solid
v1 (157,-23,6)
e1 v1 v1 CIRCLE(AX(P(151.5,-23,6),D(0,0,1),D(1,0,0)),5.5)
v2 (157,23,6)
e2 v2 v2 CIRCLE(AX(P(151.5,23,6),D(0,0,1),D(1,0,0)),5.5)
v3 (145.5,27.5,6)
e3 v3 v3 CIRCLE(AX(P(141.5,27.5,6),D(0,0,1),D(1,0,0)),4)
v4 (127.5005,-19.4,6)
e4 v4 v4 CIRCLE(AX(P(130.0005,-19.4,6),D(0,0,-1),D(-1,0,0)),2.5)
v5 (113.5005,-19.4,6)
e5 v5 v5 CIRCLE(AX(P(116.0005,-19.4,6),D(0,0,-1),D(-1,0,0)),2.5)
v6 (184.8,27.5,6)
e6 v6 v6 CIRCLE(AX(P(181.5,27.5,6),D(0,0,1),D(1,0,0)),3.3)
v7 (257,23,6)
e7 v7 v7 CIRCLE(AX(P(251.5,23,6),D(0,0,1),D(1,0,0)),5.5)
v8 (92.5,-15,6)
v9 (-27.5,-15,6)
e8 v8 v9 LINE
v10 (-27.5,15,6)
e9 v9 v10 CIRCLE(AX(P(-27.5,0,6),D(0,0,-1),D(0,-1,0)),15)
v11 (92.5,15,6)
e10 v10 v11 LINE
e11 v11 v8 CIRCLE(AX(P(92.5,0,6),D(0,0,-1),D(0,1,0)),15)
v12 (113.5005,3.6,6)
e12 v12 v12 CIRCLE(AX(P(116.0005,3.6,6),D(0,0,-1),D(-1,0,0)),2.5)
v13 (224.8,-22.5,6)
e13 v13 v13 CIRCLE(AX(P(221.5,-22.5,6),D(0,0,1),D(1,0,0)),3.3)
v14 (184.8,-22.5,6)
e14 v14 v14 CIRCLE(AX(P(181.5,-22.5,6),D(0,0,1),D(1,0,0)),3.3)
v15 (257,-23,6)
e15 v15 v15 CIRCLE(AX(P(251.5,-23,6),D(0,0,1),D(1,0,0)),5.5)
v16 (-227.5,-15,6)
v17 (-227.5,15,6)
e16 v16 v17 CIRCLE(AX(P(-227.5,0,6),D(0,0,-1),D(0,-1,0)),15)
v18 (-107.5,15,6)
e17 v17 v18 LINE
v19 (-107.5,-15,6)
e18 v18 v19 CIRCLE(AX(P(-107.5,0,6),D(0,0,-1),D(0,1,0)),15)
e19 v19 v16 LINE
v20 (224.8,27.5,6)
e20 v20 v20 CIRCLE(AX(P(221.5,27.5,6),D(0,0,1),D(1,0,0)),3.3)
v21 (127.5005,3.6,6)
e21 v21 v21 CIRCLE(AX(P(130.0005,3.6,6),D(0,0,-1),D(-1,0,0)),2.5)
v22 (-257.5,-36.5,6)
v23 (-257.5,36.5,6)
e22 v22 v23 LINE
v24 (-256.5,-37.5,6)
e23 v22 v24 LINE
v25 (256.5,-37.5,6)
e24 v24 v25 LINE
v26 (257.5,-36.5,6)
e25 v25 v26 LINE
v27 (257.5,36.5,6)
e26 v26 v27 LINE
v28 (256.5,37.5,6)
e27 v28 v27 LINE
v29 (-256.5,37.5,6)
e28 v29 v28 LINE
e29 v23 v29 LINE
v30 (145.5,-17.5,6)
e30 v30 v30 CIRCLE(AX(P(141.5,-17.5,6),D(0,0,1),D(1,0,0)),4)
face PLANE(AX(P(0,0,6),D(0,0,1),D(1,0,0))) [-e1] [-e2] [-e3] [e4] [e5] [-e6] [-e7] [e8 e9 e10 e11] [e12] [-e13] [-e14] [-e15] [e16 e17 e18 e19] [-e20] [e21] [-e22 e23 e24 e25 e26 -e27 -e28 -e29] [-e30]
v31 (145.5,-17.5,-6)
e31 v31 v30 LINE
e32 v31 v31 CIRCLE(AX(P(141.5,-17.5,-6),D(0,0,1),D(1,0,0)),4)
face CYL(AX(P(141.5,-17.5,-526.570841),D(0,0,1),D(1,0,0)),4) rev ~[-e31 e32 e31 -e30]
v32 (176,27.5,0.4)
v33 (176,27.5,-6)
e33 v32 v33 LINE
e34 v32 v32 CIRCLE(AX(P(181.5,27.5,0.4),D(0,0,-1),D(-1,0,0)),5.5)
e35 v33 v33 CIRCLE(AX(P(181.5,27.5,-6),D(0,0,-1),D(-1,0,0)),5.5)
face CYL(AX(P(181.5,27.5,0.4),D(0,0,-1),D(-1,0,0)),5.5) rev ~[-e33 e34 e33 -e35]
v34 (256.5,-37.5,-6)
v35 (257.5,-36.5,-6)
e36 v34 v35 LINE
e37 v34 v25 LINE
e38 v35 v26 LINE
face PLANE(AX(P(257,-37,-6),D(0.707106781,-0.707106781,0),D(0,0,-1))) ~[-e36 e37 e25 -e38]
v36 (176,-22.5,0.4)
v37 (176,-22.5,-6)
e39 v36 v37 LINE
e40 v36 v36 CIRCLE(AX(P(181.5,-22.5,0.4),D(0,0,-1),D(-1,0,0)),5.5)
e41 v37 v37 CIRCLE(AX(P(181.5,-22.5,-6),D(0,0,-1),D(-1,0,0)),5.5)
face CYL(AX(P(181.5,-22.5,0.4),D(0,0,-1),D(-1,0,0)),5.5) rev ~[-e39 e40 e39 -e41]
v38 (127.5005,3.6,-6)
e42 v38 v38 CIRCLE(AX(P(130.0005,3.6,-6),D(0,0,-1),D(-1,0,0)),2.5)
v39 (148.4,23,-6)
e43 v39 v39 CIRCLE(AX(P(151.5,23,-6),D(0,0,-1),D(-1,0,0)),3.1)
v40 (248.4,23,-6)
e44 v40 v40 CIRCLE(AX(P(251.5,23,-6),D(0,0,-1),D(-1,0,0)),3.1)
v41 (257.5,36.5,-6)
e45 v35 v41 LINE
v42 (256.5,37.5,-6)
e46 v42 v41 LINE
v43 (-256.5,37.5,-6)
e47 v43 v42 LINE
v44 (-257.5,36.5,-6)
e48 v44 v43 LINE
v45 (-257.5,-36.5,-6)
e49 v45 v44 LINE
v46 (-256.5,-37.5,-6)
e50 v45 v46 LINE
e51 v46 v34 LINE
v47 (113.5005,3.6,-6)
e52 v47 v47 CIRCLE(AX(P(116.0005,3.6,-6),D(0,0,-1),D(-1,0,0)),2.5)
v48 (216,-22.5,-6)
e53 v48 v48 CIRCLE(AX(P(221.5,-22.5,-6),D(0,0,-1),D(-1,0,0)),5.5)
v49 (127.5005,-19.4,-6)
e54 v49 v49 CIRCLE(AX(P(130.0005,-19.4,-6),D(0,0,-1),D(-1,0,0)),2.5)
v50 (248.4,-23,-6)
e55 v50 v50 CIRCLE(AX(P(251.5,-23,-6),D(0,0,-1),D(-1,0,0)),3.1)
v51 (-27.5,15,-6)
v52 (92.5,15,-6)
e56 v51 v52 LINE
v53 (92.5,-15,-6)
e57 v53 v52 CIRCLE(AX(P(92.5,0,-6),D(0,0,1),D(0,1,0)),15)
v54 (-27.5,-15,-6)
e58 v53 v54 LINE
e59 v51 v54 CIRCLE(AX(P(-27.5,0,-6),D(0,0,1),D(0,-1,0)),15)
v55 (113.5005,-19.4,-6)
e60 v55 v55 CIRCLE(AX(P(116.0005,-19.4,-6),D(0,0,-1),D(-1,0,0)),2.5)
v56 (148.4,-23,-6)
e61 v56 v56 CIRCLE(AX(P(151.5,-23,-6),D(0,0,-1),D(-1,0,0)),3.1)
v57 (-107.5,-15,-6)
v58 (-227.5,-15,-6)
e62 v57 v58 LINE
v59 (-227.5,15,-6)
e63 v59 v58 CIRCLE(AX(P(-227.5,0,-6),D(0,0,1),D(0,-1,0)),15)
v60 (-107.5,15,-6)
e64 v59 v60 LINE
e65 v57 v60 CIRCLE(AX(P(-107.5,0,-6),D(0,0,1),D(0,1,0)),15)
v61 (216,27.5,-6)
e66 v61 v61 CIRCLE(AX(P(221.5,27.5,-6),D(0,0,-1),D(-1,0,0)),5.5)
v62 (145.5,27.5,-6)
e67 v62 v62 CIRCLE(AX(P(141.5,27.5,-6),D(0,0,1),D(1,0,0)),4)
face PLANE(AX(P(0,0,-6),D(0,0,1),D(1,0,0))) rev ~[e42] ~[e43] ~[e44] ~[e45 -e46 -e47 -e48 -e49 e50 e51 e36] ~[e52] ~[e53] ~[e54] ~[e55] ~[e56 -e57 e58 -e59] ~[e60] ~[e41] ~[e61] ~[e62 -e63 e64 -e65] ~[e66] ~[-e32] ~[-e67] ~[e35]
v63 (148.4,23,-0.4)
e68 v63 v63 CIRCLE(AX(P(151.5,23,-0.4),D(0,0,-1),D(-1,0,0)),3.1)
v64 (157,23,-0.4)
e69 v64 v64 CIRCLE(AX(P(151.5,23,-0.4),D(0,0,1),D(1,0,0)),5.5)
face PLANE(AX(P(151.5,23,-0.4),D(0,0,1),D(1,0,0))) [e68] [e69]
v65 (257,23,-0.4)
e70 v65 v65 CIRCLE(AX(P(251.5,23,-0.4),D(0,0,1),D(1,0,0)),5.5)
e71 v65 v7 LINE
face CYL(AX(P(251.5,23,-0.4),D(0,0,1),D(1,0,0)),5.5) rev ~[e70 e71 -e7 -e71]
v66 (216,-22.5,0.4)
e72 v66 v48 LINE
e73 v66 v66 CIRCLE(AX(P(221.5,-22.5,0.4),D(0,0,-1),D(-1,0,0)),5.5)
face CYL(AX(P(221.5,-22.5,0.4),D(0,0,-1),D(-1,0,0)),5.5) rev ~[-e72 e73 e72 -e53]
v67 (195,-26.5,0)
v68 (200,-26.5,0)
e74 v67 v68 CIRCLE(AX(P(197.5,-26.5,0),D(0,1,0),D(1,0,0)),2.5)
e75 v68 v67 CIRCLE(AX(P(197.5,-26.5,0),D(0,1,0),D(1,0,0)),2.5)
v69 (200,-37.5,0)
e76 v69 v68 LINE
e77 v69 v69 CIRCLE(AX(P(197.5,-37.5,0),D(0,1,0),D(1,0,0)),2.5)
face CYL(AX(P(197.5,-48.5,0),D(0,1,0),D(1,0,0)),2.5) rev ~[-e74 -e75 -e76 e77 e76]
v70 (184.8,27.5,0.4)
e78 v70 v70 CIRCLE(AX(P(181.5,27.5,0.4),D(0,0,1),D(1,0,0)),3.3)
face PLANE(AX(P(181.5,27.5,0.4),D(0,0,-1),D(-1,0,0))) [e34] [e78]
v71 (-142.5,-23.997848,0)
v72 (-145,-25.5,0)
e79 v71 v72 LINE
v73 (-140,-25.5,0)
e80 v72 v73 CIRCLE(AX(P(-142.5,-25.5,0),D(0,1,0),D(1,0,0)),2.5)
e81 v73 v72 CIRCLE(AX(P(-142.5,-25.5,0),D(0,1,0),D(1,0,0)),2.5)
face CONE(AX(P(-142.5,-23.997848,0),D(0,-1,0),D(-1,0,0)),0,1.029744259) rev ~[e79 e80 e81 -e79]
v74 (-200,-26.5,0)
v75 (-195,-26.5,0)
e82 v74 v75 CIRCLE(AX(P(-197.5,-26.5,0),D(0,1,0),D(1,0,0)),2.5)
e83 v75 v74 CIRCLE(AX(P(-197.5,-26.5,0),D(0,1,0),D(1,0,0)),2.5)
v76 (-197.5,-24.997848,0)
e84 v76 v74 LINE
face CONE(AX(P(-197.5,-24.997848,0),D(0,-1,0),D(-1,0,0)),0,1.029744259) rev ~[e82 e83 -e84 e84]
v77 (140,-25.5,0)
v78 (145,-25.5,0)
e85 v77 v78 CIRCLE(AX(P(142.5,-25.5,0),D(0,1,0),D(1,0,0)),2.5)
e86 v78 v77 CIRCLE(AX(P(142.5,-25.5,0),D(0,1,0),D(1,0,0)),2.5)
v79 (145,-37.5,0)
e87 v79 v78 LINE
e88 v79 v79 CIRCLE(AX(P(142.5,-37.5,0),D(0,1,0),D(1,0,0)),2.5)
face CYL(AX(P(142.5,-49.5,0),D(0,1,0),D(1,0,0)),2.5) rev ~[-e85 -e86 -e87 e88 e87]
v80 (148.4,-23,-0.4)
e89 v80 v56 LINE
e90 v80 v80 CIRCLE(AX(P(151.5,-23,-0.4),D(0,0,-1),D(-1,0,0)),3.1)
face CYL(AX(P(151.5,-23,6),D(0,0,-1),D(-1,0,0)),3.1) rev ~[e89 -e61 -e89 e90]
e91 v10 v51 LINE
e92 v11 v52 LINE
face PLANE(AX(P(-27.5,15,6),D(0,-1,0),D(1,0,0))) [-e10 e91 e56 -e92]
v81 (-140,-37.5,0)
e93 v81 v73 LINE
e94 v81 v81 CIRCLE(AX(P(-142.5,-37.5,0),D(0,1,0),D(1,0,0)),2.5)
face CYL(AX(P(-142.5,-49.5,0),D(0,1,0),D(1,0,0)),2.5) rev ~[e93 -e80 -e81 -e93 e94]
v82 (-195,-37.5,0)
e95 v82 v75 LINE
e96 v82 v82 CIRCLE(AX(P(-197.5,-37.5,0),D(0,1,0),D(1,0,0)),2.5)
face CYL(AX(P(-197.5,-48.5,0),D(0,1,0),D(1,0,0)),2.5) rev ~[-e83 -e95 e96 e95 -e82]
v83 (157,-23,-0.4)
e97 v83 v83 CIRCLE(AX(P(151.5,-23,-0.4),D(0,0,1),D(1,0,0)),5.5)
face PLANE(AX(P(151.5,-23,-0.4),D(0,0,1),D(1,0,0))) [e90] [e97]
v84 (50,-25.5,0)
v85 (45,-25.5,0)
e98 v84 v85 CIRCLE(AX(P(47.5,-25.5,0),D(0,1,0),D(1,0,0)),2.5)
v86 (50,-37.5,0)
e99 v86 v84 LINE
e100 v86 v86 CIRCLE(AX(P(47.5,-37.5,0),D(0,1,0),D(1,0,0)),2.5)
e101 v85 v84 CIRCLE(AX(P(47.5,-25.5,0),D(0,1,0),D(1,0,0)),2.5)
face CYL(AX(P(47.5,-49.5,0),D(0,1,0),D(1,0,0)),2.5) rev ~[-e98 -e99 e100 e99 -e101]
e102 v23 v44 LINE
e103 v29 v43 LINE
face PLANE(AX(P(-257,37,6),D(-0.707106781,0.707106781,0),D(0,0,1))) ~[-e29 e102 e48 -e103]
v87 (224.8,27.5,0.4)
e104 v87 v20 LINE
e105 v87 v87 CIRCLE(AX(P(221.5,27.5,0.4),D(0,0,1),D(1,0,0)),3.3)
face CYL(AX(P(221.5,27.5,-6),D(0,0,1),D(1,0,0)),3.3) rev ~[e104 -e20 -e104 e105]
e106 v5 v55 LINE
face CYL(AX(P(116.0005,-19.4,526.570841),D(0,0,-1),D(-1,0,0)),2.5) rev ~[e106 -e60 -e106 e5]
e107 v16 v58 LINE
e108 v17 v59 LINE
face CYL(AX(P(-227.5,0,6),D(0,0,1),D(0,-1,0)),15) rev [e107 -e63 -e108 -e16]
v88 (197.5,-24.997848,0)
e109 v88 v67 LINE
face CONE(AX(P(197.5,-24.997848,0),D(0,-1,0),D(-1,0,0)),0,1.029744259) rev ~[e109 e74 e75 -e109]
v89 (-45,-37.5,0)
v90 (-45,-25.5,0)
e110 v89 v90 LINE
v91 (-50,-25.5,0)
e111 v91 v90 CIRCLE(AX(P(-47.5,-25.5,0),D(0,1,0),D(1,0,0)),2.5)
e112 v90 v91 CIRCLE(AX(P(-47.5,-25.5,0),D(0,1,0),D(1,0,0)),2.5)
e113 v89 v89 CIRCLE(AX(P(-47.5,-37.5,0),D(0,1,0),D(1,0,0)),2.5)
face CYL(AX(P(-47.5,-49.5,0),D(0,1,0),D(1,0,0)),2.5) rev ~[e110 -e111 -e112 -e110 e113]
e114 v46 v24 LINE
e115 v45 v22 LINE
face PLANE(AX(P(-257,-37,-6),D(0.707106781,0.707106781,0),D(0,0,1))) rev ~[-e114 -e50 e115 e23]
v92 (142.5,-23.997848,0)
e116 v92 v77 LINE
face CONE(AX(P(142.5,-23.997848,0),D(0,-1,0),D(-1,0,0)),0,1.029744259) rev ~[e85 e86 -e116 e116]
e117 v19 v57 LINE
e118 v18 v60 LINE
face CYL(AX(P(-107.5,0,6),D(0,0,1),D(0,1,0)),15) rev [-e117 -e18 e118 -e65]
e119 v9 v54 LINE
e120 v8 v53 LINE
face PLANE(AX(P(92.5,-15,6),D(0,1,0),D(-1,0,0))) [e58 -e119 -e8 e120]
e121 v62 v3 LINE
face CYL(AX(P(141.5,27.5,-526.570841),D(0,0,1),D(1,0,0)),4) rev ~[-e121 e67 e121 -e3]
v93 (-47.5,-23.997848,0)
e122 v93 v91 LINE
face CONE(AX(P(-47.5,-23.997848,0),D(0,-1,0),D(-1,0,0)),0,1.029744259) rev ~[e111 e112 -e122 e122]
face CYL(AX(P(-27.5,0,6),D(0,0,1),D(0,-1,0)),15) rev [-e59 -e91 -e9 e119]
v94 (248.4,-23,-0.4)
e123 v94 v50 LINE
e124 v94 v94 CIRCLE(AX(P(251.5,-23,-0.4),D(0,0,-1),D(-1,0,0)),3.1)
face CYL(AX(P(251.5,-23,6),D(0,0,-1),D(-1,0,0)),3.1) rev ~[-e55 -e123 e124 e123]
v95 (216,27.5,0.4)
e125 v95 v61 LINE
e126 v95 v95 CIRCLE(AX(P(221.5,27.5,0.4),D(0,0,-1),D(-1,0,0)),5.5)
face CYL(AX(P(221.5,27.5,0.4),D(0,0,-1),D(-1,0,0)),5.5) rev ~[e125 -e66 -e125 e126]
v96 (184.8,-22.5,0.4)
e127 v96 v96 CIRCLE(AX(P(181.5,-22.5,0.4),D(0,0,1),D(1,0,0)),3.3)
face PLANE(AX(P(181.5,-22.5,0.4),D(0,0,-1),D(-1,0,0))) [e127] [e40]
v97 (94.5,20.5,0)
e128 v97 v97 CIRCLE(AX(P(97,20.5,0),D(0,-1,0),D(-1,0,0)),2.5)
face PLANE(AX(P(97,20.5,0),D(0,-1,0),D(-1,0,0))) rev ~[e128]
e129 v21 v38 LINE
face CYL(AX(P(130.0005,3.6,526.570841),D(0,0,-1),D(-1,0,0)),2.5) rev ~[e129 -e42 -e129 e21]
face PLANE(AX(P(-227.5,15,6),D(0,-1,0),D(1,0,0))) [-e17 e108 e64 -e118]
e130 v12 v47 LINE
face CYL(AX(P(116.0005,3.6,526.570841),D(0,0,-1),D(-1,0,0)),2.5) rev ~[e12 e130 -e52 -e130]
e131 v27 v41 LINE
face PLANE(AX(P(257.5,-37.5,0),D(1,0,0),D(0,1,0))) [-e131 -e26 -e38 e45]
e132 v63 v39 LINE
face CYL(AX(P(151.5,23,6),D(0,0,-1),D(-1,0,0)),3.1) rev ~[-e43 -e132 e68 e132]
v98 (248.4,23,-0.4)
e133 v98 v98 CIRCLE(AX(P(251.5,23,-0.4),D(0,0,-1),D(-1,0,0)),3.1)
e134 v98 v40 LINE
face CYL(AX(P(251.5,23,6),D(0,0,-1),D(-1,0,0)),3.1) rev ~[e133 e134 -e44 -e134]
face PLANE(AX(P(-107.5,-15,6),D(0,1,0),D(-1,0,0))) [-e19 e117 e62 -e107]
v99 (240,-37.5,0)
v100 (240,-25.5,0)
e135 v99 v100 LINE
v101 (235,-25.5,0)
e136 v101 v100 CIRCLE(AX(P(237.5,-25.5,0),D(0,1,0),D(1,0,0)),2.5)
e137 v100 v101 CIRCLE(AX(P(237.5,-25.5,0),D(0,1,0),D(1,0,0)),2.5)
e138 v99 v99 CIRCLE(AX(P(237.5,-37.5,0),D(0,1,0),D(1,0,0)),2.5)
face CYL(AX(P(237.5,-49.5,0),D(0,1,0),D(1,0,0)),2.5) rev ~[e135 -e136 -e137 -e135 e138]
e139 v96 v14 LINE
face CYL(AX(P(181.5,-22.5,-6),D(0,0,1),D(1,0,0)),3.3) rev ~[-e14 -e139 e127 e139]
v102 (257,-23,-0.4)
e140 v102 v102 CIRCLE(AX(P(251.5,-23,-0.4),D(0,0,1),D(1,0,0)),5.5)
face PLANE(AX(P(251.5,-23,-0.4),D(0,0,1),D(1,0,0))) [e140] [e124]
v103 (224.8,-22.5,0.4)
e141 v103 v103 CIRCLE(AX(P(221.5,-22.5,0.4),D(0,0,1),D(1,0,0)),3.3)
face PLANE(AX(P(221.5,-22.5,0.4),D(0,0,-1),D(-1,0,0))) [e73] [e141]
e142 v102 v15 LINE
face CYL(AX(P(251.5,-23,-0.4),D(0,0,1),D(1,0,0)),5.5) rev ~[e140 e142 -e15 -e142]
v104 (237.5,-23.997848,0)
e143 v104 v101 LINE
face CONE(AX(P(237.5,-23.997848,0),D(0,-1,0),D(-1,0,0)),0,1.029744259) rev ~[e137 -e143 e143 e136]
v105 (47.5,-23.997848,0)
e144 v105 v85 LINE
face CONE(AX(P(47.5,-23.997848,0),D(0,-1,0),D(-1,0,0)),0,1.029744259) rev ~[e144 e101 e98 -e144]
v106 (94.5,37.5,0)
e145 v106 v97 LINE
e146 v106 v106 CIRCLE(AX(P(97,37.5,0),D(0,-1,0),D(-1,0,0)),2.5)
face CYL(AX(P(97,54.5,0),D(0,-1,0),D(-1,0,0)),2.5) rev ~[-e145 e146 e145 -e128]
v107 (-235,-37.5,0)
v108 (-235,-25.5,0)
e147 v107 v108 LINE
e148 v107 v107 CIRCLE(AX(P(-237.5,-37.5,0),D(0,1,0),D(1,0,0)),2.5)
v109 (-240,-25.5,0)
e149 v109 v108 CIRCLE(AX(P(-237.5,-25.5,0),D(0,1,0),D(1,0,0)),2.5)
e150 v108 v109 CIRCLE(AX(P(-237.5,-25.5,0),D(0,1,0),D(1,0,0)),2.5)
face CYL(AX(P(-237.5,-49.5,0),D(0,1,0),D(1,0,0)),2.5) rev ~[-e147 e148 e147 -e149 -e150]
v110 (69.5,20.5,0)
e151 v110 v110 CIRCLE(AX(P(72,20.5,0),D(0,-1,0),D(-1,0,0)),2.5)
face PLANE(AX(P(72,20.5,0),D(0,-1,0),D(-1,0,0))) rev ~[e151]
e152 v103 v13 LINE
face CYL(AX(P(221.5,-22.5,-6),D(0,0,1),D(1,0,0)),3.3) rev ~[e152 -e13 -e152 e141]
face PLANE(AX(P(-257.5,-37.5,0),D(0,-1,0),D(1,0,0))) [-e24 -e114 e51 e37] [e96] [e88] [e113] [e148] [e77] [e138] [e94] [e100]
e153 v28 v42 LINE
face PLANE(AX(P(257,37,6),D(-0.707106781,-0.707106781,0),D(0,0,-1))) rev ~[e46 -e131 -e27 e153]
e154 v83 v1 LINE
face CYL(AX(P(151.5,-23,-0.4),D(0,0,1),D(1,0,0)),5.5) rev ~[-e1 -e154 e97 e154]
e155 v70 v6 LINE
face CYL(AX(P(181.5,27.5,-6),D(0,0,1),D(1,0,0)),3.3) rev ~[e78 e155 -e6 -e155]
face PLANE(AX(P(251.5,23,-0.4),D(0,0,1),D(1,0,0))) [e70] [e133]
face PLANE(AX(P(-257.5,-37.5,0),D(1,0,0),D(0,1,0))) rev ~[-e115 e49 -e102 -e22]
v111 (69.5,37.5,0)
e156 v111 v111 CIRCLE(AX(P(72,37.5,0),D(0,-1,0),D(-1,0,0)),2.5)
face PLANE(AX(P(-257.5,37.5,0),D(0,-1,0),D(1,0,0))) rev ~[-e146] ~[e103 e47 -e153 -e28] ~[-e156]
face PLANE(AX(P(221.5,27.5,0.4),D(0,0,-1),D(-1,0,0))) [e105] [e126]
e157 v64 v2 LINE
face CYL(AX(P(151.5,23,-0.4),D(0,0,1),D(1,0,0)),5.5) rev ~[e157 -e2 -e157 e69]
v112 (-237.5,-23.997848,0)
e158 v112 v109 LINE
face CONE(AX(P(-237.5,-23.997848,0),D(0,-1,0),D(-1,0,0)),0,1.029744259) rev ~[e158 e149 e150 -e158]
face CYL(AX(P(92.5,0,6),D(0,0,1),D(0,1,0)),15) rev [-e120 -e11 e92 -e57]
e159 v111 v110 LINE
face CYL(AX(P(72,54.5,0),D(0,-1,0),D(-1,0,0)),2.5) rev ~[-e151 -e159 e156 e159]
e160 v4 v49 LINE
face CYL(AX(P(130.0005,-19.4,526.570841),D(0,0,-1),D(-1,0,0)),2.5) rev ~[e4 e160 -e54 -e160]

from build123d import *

# Parameters (mm, degrees)
SKETCH1_W                                           = 515
SKETCH1_H                                           = 75
BOSS_EXTRUDE1_DEPTH                                 = 6
M6_TAPPED_HOLE1_D                                   = 5
M6_TAPPED_HOLE1_DEPTH                               = 17
BLIND_PIN_HOLE2_D                                   = 8
CBORE_FOR_M6_HEX_SOCKET_HEAD_CAP_SCREW1_D           = 6.2
CBORE_FOR_M6_HEX_SOCKET_HEAD_CAP_SCREW1_CBORE_D     = 11
CBORE_FOR_M6_HEX_SOCKET_HEAD_CAP_SCREW1_CBORE_DEPTH = 6.4
M6_TAPPED_HOLE2_D                                   = 5
M6_TAPPED_HOLE3_D                                   = 5
M6_TAPPED_HOLE3_DEPTH                               = 12
M6_TAPPED_HOLE3_TIP                                 = 1.502151548
MM_2_D                                              = 5
MM_2_DEPTH                                          = 11
MM_2_TIP                                            = 1.502151548
CBORE_FOR_M6_HEX_SOCKET_HEAD_CAP_SCREW2_D           = 6.6
CBORE_FOR_M6_HEX_SOCKET_HEAD_CAP_SCREW2_CBORE_D     = 11
CBORE_FOR_M6_HEX_SOCKET_HEAD_CAP_SCREW2_CBORE_DEPTH = 6.4
CUT_EXTRUDE1_DEPTH                                  = 261.492802204
CHAMFER1_SIZE                                       = 1


with BuildPart() as part:
    # Sketch1 → Boss-Extrude1 (new, symmetric)
    with BuildSketch(Plane.XY):
        Rectangle(SKETCH1_W, SKETCH1_H)
    extrude(amount=BOSS_EXTRUDE1_DEPTH, both=True)

    # M6 Tapped Hole1
    with Locations(Plane(origin=(0, 37.5, 0), x_dir=(1, 0, 0), z_dir=(0, 1, 0))):
        with Locations((72, 0), (97, 0)):
            Hole(M6_TAPPED_HOLE1_D / 2, depth=M6_TAPPED_HOLE1_DEPTH)

    # Blind pin hole2 (through all)
    with Locations(Plane(origin=(0, 0, -6), x_dir=(-1, 0, 0), z_dir=(0, 0, -1))):
        with Locations((-141.5, 27.5), (-141.5, -17.5)):
            Hole(BLIND_PIN_HOLE2_D / 2)

    # CBORE for M6 Hex Socket Head Cap Screw1 (through all)
    with Locations(Plane.XY.offset(6)):
        with Locations((151.5, 23), (151.5, -23), (251.5, 23), (251.5, -23)):
            CounterBoreHole(CBORE_FOR_M6_HEX_SOCKET_HEAD_CAP_SCREW1_D / 2, CBORE_FOR_M6_HEX_SOCKET_HEAD_CAP_SCREW1_CBORE_D / 2, CBORE_FOR_M6_HEX_SOCKET_HEAD_CAP_SCREW1_CBORE_DEPTH)

    # M6 Tapped Hole2 (through all)
    with Locations(Plane.XY.offset(6)):
        with Locations((116.0005, 3.6), (130.0005, 3.6), (116.0005, -19.4), (130.0005, -19.4)):
            Hole(M6_TAPPED_HOLE2_D / 2)

    # M6 Tapped Hole3
    with Locations(Plane(origin=(0, -37.5, 0), x_dir=(-1, 0, 0), z_dir=(0, -1, 0))):
        with Locations((237.5, 0), (142.5, 0), (47.5, 0), (-47.5, 0), (-142.5, 0), (-237.5, 0)):
            Hole(M6_TAPPED_HOLE3_D / 2, depth=M6_TAPPED_HOLE3_DEPTH)
            with Locations((0, 0, -(M6_TAPPED_HOLE3_DEPTH + M6_TAPPED_HOLE3_TIP / 2))):  # 118° drill point
                Cone(0, M6_TAPPED_HOLE3_D / 2, M6_TAPPED_HOLE3_TIP, mode=Mode.SUBTRACT)

    # 大小mm 暗销孔2
    with Locations(Plane(origin=(0, -37.5, 0), x_dir=(-1, 0, 0), z_dir=(0, -1, 0))):
        with Locations((-197.5, 0), (197.5, 0)):
            Hole(MM_2_D / 2, depth=MM_2_DEPTH)
            with Locations((0, 0, -(MM_2_DEPTH + MM_2_TIP / 2))):  # 118° drill point
                Cone(0, MM_2_D / 2, MM_2_TIP, mode=Mode.SUBTRACT)

    # CBORE for M6 Hex Socket Head Cap Screw2 (through all)
    with Locations(Plane(origin=(0, 0, -6), x_dir=(-1, 0, 0), z_dir=(0, 0, -1))):
        with Locations((-221.5, 27.5), (-181.5, 27.5), (-181.5, -22.5), (-221.5, -22.5)):
            CounterBoreHole(CBORE_FOR_M6_HEX_SOCKET_HEAD_CAP_SCREW2_D / 2, CBORE_FOR_M6_HEX_SOCKET_HEAD_CAP_SCREW2_CBORE_D / 2, CBORE_FOR_M6_HEX_SOCKET_HEAD_CAP_SCREW2_CBORE_DEPTH)

    # Sketch18 → Cut-Extrude1 (cut, through all)
    with BuildSketch(Plane.XY.offset(6)):
        with BuildLine():
            Line((-227.5, 15), (-107.5, 15))
            ThreePointArc((-107.5, 15), (-92.5, 0), (-107.5, -15))
            Line((-107.5, -15), (-227.5, -15))
            ThreePointArc((-227.5, -15), (-242.5, 0), (-227.5, 15))
        make_face()
        with BuildLine():
            Line((-27.5, 15), (92.5, 15))
            ThreePointArc((92.5, 15), (107.5, 0), (92.5, -15))
            Line((92.5, -15), (-27.5, -15))
            ThreePointArc((-27.5, -15), (-42.5, 0), (-27.5, 15))
        make_face()
    extrude(amount=-CUT_EXTRUDE1_DEPTH, mode=Mode.SUBTRACT)

    # Chamfer1
    chamfer1_edges = [part.edges().sort_by_distance(p)[0] for p in [
        (257.5, -37.5, 0),
        (-257.5, -37.5, 0),
        (-257.5, 37.5, 0),
        (257.5, 37.5, 0),
    ]]
    chamfer(chamfer1_edges, length=CHAMFER1_SIZE)


solid = part.part
